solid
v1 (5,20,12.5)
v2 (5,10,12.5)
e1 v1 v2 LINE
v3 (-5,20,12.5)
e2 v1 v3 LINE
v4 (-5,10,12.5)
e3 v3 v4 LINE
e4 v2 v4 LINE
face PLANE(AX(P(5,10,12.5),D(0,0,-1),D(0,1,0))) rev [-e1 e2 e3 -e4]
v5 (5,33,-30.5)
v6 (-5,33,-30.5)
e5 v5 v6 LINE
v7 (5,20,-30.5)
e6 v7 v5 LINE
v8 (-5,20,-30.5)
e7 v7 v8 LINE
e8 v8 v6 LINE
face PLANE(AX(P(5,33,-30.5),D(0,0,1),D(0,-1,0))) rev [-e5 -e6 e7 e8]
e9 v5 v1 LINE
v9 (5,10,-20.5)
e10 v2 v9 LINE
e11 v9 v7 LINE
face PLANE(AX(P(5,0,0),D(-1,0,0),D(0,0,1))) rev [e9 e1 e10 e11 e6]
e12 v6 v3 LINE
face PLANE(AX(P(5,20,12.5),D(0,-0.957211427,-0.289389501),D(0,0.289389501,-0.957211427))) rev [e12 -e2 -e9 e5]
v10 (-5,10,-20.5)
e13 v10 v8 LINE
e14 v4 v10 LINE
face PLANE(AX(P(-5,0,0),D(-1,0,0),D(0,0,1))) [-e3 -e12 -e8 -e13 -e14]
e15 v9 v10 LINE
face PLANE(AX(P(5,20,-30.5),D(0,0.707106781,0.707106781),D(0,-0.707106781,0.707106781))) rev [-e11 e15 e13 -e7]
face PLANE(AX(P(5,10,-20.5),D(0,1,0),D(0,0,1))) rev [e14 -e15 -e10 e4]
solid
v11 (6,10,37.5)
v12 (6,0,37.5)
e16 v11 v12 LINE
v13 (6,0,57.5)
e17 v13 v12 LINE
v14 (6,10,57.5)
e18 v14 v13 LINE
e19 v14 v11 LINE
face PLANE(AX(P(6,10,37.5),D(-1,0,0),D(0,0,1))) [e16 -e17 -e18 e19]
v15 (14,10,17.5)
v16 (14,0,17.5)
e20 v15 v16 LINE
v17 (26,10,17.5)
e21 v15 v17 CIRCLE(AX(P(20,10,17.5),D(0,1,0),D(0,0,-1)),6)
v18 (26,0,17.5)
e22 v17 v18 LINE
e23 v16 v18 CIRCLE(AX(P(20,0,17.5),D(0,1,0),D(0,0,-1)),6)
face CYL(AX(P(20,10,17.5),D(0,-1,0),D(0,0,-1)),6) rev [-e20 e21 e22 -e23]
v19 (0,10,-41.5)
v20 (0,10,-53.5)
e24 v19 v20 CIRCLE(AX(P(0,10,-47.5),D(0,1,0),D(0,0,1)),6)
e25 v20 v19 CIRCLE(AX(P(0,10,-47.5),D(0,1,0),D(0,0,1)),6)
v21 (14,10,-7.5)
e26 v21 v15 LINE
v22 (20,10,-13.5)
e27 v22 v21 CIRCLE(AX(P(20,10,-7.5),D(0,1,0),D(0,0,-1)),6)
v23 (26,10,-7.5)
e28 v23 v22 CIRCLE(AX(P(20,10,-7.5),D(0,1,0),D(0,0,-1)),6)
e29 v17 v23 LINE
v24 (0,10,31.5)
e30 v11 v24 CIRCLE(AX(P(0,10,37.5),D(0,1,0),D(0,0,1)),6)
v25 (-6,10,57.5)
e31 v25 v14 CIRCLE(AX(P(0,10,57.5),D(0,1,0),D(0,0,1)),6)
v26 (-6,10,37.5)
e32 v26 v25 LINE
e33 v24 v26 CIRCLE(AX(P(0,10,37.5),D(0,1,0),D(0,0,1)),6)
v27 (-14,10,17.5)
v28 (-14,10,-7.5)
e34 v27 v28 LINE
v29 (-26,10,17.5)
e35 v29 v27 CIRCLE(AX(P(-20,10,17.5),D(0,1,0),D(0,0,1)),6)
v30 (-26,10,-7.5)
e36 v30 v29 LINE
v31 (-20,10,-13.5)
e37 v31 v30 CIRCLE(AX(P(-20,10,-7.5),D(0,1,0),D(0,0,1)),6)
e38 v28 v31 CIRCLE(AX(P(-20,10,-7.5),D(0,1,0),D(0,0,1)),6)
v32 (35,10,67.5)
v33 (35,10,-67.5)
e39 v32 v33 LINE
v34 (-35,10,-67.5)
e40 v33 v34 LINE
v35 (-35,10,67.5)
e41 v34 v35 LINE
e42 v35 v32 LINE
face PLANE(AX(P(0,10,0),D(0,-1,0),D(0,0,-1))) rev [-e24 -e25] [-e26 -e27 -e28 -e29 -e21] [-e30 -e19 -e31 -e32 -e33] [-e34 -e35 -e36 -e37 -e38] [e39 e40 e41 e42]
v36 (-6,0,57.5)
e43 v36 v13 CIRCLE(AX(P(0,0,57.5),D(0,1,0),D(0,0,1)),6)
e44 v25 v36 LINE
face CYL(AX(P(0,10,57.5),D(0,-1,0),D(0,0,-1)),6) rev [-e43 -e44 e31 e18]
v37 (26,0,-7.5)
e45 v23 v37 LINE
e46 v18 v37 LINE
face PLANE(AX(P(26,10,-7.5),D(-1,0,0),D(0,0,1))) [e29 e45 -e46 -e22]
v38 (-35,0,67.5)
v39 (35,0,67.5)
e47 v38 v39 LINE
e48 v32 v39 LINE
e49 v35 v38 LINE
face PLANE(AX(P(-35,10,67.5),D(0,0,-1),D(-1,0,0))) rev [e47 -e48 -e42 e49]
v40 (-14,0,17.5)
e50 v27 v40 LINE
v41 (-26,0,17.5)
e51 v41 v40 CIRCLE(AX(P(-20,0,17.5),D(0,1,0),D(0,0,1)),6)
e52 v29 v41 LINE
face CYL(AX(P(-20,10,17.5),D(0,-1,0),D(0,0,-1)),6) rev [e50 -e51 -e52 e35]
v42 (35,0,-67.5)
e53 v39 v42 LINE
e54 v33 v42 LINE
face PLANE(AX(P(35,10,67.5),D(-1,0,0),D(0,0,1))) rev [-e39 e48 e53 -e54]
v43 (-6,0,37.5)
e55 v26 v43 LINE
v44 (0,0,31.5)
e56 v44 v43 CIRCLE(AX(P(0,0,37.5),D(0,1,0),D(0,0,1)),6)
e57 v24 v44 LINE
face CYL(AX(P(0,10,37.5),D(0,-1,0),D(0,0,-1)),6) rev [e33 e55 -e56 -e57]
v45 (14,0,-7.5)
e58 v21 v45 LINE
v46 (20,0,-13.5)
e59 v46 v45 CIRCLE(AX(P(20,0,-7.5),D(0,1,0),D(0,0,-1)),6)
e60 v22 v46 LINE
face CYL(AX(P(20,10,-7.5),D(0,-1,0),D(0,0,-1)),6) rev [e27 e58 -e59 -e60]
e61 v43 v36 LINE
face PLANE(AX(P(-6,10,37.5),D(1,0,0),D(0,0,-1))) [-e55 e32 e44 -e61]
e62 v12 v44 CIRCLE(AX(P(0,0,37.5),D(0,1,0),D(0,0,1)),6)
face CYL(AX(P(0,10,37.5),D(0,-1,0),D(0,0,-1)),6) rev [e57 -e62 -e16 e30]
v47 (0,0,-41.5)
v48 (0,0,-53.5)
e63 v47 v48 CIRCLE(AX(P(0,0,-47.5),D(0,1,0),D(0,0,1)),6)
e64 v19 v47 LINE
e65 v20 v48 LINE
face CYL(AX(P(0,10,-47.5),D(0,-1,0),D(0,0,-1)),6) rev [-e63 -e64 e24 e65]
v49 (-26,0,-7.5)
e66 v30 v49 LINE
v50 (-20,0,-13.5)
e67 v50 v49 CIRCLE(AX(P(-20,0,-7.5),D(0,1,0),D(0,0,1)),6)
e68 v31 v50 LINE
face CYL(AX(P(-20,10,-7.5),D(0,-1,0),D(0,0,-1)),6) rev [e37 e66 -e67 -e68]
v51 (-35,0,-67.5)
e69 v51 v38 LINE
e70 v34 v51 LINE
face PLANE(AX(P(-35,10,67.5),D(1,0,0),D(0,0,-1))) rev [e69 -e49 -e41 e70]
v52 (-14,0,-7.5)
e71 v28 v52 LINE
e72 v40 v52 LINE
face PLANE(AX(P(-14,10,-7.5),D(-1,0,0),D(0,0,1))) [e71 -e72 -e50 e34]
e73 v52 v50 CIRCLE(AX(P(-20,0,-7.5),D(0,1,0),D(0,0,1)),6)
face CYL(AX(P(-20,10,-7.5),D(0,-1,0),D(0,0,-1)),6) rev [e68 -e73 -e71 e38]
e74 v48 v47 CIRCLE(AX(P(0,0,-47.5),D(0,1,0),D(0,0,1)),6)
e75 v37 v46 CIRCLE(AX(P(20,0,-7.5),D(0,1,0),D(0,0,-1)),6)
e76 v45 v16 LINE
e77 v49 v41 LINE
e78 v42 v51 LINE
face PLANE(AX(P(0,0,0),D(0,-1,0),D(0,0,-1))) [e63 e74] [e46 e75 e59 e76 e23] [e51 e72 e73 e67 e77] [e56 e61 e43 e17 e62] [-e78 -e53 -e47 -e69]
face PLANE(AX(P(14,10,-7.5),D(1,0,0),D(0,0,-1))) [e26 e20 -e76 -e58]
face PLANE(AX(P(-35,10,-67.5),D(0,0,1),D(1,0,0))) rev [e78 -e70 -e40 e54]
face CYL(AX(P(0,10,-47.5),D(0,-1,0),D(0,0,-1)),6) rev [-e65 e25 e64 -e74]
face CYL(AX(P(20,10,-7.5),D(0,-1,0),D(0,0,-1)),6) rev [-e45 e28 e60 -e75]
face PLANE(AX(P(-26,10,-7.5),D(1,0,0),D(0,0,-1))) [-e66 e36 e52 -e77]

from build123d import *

# Parameters (mm, degrees)
SKETCH_1_W      = 70
SKETCH_1_H      = 135
SKETCH_1_R      = 6
EXTRUDE_1_DEPTH = 10
EXTRUDE_2_DEPTH = 5


with BuildPart() as part:
    # 草图1 → 凸台-拉伸1 (new body)
    with BuildSketch(Plane(origin=(0, 0, 0), x_dir=(1, 0, 0), z_dir=(0, 1, 0))):
        Rectangle(SKETCH_1_W, SKETCH_1_H)
        with Locations(Location((0, 47.5, 0), (0, 0, 270))):
            Circle(SKETCH_1_R, mode=Mode.SUBTRACT)
        with BuildLine():
            Line((6, -37.5), (6, -57.5))
            ThreePointArc((6, -57.5), (0, -63.5), (-6, -57.5))
            Line((-6, -57.5), (-6, -37.5))
            ThreePointArc((-6, -37.5), (0, -31.5), (6, -37.5))
        make_face(mode=Mode.SUBTRACT)
        with BuildLine():
            Line((-14, 7.5), (-14, -17.5))
            ThreePointArc((-14, -17.5), (-20, -23.5), (-26, -17.5))
            Line((-26, -17.5), (-26, 7.5))
            ThreePointArc((-26, 7.5), (-20, 13.5), (-14, 7.5))
        make_face(mode=Mode.SUBTRACT)
        with BuildLine():
            Line((14, 7.5), (14, -17.5))
            ThreePointArc((14, -17.5), (20, -23.5), (26, -17.5))
            Line((26, -17.5), (26, 7.5))
            ThreePointArc((26, 7.5), (20, 13.5), (14, 7.5))
        make_face(mode=Mode.SUBTRACT)
    extrude(amount=EXTRUDE_1_DEPTH)


with BuildPart() as body_2:
    # 草图2 → 凸台-拉伸2 (new, symmetric)
    with BuildSketch(Plane(origin=(0, 0, 0), x_dir=(0, 0, -1), z_dir=(1, 0, 0))):
        Polygon((-12.5, 10), (-12.5, 20), (30.5, 33), (30.5, 20), (20.5, 10), align=None)
    extrude(amount=EXTRUDE_2_DEPTH, both=True)


solid = Compound([part.part, body_2.part])
